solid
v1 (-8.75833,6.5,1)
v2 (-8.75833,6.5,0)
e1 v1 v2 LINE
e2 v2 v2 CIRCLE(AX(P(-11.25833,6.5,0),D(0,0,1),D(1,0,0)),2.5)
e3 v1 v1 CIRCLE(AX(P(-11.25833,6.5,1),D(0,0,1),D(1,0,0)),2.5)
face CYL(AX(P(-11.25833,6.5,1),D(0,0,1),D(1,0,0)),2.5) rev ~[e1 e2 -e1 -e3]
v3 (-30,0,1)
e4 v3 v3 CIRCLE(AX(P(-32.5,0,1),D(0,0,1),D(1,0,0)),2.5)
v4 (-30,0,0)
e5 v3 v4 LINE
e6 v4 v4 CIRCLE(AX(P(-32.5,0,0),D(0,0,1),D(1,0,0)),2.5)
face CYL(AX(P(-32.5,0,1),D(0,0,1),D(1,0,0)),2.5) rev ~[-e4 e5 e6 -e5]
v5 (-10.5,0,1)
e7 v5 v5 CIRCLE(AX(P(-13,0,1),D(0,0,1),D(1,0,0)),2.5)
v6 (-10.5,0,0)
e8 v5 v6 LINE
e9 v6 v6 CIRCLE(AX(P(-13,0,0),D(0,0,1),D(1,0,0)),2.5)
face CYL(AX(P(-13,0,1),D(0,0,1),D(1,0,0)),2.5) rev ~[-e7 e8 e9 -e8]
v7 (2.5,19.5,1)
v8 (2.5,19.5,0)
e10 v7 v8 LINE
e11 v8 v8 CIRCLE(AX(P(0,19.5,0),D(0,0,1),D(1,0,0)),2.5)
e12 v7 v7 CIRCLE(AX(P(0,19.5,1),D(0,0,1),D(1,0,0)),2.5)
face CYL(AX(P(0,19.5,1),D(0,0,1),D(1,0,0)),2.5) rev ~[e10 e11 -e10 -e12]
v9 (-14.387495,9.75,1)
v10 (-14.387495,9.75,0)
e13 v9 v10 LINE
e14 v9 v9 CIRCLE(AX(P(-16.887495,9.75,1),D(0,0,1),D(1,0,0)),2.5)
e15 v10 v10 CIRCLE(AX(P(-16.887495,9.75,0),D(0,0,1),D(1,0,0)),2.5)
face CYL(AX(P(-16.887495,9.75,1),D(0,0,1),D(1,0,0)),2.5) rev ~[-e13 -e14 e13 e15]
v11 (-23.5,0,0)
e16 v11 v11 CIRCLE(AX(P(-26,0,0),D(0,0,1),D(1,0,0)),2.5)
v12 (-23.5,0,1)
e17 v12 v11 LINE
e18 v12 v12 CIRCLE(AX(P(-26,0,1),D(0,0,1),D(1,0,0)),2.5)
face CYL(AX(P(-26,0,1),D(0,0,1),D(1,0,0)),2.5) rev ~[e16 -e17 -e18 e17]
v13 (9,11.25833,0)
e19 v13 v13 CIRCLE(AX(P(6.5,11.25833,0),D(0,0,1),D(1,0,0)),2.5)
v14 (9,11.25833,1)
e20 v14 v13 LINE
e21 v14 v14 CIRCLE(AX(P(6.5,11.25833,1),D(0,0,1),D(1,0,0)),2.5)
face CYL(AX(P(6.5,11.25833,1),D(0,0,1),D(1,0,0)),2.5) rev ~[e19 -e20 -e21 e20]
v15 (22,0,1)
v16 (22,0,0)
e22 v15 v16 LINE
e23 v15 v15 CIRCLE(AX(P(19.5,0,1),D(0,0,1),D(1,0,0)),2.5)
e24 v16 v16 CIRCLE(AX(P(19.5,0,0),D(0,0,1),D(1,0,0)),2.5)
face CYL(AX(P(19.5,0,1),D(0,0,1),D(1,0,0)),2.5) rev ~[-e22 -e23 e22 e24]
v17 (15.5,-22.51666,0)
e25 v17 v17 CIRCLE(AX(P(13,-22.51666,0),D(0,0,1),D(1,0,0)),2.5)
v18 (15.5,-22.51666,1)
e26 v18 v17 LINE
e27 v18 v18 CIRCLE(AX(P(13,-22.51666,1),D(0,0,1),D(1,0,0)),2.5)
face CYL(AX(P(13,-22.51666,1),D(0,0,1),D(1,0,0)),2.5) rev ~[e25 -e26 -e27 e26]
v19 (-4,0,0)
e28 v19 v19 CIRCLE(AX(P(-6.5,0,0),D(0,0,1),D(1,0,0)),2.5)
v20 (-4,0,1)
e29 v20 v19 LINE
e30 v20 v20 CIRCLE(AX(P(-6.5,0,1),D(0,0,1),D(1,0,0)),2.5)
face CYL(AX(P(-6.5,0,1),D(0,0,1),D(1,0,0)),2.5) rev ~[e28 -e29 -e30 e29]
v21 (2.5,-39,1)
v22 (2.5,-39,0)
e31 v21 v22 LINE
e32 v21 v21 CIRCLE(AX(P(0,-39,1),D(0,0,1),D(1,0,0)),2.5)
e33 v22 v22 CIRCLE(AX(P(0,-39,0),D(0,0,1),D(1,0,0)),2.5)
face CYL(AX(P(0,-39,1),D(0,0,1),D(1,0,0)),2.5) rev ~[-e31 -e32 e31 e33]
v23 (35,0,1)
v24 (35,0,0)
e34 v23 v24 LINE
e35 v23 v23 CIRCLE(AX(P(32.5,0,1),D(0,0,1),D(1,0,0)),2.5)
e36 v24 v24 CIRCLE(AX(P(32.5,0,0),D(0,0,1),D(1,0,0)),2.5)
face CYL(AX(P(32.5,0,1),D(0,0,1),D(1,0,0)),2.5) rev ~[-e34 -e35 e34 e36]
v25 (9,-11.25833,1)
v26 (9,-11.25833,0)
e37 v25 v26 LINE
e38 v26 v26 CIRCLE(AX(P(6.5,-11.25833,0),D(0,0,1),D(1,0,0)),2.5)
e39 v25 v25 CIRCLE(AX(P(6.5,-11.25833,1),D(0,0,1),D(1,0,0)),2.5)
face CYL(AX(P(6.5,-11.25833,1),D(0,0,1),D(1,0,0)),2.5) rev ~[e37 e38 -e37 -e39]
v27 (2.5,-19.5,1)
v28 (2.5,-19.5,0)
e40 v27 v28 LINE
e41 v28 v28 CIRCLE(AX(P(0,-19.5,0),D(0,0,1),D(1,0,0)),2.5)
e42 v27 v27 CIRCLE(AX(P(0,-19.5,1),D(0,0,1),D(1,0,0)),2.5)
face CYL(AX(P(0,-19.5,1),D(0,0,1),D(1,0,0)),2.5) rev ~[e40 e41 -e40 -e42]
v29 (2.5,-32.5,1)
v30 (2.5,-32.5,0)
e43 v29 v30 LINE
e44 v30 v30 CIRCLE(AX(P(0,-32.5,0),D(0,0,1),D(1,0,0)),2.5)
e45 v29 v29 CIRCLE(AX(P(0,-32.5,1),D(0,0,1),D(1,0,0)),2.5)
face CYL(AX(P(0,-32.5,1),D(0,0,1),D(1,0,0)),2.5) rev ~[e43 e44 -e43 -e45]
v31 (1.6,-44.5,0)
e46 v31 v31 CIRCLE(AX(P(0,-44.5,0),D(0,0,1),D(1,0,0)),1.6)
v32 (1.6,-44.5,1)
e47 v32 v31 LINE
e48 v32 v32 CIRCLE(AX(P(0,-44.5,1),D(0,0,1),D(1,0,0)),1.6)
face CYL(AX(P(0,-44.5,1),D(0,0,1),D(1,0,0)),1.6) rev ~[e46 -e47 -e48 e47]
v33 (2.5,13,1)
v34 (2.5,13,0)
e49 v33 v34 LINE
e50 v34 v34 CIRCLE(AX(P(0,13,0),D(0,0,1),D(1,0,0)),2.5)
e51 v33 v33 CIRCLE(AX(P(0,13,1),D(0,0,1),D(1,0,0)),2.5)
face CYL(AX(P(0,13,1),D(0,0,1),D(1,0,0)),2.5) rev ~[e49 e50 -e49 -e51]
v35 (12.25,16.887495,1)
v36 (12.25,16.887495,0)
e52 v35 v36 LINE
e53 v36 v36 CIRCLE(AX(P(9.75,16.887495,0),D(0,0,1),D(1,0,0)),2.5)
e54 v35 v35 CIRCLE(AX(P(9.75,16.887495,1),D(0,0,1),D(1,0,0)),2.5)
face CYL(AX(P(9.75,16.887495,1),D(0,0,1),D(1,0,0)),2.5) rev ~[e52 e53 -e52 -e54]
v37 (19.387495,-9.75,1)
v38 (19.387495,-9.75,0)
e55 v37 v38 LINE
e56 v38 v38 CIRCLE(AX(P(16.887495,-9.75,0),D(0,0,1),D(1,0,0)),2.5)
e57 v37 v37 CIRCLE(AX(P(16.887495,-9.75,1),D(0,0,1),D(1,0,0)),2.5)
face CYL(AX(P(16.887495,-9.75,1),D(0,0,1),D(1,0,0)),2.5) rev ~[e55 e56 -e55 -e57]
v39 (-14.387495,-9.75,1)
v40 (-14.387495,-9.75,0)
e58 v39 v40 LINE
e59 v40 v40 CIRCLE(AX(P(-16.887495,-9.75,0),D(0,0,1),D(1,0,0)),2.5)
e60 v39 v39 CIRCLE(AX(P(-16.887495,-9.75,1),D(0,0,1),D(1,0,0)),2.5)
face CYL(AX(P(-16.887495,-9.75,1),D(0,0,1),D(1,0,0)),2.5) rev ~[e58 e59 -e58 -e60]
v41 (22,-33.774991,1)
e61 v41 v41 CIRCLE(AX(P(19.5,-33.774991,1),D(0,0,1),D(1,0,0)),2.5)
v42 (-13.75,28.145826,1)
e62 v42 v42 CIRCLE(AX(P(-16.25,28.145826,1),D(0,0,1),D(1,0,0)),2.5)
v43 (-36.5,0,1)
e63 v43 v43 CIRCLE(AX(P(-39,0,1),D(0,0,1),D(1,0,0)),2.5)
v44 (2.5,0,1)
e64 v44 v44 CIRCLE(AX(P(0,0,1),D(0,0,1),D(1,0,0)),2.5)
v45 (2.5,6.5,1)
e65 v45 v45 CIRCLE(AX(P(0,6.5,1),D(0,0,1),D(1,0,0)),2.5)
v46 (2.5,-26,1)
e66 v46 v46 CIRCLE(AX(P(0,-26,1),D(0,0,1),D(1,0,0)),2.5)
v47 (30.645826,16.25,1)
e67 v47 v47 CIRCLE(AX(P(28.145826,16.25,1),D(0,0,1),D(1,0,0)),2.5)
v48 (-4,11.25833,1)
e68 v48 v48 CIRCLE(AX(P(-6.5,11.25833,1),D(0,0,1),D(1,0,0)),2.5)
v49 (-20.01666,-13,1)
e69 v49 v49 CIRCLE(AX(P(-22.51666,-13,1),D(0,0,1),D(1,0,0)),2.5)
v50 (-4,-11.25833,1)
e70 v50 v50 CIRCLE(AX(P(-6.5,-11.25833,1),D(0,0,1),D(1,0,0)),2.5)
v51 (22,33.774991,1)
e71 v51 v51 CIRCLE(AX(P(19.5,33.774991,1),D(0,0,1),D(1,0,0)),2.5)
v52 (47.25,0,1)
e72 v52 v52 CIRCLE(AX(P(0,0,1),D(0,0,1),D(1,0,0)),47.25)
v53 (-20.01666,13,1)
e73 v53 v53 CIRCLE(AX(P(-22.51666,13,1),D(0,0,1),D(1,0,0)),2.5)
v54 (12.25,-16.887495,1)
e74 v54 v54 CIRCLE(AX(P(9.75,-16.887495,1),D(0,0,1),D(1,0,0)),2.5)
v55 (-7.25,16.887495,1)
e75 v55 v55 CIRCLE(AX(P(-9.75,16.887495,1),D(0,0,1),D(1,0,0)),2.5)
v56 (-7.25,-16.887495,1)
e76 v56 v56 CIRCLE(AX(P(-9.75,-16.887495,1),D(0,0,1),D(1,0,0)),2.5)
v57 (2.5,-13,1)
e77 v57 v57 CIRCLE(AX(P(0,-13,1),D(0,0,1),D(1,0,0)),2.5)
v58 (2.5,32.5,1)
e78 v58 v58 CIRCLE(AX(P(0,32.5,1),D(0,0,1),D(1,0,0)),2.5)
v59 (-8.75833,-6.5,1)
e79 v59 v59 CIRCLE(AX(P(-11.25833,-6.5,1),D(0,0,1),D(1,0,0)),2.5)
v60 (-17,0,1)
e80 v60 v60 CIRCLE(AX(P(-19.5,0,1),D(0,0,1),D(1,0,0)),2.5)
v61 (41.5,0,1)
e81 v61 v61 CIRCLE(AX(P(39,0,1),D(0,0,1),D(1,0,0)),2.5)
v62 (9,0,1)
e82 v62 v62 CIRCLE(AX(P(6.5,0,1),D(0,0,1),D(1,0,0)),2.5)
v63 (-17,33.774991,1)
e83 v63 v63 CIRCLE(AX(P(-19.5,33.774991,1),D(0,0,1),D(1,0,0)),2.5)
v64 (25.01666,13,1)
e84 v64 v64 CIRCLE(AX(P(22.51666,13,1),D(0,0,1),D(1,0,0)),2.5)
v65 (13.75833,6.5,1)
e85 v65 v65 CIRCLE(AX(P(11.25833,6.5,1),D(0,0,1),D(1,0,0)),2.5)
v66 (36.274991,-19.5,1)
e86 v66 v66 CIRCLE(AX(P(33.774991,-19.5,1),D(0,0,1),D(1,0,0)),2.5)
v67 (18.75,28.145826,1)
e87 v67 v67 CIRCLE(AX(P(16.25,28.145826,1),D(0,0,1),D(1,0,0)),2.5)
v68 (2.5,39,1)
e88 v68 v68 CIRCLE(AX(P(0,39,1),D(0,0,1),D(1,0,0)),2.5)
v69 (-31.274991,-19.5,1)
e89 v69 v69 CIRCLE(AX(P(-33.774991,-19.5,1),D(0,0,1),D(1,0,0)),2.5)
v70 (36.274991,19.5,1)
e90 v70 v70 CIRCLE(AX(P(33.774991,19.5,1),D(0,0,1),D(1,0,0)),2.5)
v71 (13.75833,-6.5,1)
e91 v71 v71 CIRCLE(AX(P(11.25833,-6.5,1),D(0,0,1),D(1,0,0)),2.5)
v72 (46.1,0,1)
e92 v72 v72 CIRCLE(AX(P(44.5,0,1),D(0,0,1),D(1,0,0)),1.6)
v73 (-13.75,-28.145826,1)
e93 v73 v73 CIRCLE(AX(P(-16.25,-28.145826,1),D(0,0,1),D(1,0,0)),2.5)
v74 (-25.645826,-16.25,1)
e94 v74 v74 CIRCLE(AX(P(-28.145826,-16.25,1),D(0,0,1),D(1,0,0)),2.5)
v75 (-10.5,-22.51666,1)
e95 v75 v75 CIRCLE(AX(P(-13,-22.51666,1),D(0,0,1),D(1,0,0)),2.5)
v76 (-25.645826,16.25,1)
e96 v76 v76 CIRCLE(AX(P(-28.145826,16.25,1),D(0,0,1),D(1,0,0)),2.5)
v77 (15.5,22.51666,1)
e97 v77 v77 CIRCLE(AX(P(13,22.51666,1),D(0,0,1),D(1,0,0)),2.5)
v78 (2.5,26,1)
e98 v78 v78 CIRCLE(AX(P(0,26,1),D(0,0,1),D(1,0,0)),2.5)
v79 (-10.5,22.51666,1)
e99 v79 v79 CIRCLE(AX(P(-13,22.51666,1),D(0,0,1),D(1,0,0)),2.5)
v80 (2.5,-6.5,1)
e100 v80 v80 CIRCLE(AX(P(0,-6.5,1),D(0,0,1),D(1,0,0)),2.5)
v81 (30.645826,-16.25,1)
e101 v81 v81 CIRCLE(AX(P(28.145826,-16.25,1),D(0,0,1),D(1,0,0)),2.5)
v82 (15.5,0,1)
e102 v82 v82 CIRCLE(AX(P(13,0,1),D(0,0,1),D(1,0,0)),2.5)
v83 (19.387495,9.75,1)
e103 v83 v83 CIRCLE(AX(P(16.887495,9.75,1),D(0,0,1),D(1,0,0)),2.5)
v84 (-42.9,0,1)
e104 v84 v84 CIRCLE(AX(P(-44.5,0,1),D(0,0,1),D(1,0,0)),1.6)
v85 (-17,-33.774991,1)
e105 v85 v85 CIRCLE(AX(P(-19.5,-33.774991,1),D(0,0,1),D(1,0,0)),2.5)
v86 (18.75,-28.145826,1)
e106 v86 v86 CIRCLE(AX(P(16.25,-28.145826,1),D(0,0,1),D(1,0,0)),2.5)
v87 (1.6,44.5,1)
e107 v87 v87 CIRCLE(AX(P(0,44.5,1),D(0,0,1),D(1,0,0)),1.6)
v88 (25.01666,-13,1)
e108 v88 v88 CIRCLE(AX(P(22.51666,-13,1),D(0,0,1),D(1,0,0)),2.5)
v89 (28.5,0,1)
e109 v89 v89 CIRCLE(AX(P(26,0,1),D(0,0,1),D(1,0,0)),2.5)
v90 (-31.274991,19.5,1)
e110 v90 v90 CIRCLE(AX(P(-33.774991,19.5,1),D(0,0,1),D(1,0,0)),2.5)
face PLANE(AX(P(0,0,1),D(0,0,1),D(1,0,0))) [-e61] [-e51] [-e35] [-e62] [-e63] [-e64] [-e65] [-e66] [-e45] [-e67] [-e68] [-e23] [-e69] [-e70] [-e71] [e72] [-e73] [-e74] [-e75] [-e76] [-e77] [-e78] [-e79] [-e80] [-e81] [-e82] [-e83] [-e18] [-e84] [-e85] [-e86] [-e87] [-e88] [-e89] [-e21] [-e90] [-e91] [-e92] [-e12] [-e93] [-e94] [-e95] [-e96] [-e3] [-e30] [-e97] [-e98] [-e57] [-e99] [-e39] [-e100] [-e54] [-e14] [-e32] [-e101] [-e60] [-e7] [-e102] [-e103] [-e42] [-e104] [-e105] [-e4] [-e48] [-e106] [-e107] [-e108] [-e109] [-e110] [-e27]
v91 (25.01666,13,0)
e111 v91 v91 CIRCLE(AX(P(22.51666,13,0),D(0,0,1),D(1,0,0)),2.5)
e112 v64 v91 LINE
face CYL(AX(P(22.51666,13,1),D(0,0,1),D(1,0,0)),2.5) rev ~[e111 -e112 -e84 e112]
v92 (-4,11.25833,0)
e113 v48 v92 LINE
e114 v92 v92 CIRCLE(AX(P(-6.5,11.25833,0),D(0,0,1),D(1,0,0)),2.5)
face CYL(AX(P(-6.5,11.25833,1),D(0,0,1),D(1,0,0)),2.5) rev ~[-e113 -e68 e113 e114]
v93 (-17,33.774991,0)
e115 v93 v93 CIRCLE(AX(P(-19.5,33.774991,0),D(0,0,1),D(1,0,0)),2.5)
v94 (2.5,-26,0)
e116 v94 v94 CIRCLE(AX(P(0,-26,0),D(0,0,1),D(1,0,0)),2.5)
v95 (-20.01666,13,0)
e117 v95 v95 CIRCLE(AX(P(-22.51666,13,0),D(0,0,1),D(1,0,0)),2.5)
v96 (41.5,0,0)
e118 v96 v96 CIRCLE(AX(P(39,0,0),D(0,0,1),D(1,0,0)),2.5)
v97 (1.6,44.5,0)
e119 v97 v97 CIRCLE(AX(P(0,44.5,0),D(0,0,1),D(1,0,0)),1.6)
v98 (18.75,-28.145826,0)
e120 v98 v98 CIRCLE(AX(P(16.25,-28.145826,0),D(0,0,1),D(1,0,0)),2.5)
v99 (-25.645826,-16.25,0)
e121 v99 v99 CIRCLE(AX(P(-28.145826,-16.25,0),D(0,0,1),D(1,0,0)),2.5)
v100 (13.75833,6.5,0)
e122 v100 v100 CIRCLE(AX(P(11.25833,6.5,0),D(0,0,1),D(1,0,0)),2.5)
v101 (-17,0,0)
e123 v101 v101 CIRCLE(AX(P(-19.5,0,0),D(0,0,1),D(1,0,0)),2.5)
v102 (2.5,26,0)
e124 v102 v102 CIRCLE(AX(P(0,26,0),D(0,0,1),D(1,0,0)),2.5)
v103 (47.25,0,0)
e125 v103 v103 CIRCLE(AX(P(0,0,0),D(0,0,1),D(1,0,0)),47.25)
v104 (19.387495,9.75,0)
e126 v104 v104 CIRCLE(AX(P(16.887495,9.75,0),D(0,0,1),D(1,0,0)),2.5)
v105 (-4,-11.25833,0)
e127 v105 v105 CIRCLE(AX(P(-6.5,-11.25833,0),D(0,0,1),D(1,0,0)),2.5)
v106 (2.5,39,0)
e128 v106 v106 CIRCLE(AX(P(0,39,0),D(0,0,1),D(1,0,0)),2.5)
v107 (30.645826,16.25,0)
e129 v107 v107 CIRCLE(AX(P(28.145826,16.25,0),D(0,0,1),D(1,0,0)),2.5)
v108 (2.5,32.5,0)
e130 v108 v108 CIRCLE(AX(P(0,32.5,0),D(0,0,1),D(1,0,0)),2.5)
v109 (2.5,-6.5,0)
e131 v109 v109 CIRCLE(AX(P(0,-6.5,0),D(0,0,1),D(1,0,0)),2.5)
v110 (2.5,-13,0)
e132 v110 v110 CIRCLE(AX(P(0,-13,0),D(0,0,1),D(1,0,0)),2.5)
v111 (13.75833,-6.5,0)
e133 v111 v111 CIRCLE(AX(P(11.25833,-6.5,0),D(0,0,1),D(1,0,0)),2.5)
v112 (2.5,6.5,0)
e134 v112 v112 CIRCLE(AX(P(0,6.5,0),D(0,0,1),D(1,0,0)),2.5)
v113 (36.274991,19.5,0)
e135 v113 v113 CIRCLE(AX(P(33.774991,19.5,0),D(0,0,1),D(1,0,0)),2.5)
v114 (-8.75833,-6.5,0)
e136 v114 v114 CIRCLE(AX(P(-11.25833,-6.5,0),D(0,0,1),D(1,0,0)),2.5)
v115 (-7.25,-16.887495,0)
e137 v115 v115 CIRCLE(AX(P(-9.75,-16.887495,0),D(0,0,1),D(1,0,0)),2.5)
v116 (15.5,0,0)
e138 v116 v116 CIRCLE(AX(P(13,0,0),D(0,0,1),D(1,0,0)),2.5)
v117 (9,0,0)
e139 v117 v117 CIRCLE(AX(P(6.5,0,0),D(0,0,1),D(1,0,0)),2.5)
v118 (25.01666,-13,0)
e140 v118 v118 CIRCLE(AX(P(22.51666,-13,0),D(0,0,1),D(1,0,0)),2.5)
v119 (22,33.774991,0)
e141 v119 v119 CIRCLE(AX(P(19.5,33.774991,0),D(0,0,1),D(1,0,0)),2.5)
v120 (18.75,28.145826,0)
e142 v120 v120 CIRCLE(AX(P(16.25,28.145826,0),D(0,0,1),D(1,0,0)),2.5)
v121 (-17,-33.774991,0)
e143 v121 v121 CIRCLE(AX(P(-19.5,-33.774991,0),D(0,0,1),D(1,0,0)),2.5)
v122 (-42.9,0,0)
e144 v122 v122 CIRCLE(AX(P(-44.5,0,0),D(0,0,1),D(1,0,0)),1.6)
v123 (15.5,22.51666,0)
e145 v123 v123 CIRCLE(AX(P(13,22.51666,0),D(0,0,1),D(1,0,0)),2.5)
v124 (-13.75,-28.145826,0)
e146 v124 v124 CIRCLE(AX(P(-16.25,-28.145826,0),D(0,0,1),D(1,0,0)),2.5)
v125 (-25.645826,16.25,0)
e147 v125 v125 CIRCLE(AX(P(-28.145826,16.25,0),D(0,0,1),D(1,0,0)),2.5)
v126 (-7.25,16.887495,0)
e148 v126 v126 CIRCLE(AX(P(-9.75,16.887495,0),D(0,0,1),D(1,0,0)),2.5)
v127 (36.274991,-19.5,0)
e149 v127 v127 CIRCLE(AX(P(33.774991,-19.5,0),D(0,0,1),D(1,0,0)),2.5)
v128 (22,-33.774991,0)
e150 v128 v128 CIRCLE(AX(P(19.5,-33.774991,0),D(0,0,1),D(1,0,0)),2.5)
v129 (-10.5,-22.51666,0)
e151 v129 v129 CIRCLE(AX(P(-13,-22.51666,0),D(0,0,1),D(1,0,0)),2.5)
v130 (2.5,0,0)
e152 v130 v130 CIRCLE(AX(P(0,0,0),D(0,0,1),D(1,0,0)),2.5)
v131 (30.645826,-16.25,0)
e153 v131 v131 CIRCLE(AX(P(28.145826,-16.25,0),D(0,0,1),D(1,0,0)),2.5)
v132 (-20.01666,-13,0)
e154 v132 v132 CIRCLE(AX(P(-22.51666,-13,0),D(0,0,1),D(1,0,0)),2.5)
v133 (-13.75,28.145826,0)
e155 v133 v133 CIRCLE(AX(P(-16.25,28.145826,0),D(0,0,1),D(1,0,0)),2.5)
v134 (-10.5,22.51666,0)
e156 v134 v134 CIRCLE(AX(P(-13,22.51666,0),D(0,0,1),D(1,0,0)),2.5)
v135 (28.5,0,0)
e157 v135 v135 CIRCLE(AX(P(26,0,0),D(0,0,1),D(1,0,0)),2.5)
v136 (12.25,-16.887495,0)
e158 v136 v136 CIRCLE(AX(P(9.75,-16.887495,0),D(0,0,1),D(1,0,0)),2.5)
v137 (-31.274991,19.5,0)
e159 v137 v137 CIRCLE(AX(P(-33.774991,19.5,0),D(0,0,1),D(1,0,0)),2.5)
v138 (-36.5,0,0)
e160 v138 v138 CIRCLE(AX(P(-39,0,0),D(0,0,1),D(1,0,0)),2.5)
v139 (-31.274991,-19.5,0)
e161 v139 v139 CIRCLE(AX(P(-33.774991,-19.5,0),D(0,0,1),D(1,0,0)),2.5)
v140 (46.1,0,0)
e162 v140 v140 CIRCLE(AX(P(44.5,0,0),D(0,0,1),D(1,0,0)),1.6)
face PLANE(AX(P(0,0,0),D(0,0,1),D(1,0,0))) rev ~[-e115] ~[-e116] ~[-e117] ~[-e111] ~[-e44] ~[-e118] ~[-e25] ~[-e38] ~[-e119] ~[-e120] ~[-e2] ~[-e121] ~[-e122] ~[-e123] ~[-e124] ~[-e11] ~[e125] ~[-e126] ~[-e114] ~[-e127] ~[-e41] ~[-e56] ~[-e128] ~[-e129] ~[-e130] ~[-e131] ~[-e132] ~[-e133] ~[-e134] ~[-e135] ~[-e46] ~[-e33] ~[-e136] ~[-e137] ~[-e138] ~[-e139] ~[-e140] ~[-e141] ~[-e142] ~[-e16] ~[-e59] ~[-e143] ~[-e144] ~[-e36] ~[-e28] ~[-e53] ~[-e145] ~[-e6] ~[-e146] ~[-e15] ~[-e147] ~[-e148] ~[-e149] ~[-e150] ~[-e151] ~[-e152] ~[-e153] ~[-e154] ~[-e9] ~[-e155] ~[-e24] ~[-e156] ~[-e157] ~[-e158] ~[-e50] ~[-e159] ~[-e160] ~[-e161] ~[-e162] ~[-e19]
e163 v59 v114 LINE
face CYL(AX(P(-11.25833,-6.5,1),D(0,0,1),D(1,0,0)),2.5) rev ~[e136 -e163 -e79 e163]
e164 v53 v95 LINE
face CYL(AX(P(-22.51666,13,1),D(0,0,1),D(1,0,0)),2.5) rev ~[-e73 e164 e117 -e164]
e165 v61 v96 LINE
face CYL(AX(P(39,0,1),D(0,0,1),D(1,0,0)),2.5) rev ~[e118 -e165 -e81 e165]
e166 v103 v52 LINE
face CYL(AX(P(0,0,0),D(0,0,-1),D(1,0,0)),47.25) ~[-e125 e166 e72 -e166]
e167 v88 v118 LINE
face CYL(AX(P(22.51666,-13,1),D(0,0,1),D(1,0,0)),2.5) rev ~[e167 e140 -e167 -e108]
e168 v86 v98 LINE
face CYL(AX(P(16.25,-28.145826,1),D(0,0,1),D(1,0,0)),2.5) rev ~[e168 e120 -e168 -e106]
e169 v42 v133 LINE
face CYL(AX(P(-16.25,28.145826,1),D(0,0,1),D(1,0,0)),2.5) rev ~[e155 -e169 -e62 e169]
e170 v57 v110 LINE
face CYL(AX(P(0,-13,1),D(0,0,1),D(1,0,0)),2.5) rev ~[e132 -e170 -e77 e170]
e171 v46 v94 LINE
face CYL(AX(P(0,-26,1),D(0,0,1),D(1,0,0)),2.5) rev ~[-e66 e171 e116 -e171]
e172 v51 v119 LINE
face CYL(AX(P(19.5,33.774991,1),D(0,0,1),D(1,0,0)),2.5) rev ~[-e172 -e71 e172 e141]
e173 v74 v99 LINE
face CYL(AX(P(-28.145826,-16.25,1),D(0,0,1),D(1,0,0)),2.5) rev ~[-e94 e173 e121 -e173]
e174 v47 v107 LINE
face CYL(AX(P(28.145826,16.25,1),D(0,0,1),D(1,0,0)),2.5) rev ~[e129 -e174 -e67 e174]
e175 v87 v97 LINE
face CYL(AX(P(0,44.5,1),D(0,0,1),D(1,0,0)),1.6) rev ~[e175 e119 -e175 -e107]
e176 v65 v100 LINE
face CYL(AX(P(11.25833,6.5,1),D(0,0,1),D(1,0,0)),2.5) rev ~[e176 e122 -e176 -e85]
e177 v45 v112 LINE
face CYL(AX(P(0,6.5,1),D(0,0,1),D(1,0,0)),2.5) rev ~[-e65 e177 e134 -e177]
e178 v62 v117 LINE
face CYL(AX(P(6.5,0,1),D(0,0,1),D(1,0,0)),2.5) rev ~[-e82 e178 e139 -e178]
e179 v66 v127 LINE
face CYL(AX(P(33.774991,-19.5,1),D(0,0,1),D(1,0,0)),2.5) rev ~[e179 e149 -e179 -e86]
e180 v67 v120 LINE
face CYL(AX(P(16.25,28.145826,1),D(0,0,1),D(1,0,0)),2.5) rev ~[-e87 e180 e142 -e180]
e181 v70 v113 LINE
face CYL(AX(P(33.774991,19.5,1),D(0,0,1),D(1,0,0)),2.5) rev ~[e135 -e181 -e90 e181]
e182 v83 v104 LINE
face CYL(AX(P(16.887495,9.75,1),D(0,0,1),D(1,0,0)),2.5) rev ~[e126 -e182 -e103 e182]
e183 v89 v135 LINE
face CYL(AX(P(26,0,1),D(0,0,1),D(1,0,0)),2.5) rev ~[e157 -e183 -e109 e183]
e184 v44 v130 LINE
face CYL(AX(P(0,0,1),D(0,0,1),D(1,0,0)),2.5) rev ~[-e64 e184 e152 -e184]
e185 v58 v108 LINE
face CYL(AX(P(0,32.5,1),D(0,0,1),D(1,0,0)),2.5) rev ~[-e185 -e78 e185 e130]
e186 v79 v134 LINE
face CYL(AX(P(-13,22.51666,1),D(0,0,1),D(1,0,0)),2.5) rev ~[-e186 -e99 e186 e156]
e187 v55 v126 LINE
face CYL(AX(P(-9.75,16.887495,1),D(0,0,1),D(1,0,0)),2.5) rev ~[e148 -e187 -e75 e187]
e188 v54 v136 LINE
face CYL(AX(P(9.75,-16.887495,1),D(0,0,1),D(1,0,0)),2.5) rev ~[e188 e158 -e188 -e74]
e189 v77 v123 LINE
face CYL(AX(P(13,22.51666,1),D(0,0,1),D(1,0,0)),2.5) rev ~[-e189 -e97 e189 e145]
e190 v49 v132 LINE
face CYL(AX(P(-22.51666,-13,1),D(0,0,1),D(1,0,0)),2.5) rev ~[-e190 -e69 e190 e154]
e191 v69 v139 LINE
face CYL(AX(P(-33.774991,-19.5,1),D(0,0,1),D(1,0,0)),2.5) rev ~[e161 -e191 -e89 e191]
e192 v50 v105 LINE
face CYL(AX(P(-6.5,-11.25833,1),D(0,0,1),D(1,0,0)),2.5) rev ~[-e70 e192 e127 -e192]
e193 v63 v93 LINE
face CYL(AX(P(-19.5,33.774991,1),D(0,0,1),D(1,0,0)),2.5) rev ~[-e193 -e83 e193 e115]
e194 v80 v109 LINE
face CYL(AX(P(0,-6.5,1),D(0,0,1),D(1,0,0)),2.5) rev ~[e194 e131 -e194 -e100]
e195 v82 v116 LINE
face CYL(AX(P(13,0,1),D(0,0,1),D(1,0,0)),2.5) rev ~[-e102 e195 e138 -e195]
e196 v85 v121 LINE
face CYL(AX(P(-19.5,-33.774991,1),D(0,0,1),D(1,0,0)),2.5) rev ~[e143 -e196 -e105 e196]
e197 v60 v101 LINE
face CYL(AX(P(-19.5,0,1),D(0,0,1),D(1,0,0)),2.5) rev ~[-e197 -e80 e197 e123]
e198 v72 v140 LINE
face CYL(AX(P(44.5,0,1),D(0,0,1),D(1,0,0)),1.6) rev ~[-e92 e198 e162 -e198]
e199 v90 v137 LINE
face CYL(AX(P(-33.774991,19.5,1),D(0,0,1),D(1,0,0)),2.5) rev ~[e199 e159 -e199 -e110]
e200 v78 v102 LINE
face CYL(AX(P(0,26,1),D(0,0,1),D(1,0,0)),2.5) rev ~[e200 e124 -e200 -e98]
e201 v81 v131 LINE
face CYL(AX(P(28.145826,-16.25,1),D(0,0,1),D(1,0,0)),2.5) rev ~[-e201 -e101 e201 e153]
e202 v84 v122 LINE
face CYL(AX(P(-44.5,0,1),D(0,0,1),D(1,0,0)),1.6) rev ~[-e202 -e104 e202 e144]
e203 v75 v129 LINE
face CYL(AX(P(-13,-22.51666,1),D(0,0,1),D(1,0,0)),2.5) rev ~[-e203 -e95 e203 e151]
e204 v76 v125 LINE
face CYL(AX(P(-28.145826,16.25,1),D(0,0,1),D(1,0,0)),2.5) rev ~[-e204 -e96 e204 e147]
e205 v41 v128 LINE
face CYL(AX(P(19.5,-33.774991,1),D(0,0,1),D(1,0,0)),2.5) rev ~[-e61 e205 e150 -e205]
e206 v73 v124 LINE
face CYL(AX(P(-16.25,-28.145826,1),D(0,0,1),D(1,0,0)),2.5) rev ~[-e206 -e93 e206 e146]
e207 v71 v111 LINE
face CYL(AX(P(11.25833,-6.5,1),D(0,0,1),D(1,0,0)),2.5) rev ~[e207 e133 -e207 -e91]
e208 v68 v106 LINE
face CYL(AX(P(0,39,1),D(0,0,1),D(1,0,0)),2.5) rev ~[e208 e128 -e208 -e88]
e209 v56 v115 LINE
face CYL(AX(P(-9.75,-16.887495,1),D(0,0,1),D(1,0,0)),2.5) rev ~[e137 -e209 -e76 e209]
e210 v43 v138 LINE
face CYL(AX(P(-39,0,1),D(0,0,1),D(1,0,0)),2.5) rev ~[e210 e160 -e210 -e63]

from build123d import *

# Parameters (mm, degrees)
SKETCH_1_R          = 47.25
EXTRUDE_1_DEPTH     = 1
SKETCH_6_R          = 2.5
CUT_EXTRUDE_3_DEPTH = 2
SKETCH_7_R          = 1.6
CUT_EXTRUDE_4_DEPTH = 2


with BuildPart() as part:
    # 草图1 → 凸台-拉伸1 (new body)
    with BuildSketch(Plane.XY):
        Circle(SKETCH_1_R)
    extrude(amount=EXTRUDE_1_DEPTH)

    # 草图6 → 切除-拉伸3 (cut)
    with BuildSketch(Plane.XY.offset(1)):
        with Locations((0, 6.5)):
            Circle(SKETCH_6_R)
        with Locations((0, 13)):
            Circle(SKETCH_6_R)
        with Locations((0, 19.5)):
            Circle(SKETCH_6_R)
        with Locations((0, 26)):
            Circle(SKETCH_6_R)
        with Locations((0, 32.5)):
            Circle(SKETCH_6_R)
        with Locations((0, 39)):
            Circle(SKETCH_6_R)
        Circle(SKETCH_6_R)
        with Locations((19.5, 33.774990748)):
            Circle(SKETCH_6_R)
        with Locations((16.25, 28.145825623)):
            Circle(SKETCH_6_R)
        with Locations((13, 22.516660498)):
            Circle(SKETCH_6_R)
        with Locations((9.75, 16.887495374)):
            Circle(SKETCH_6_R)
        with Locations((6.5, 11.258330249)):
            Circle(SKETCH_6_R)
        with Locations((33.774990748, 19.5)):
            Circle(SKETCH_6_R)
        with Locations((28.145825623, 16.25)):
            Circle(SKETCH_6_R)
        with Locations((22.516660498, 13)):
            Circle(SKETCH_6_R)
        with Locations((16.887495374, 9.75)):
            Circle(SKETCH_6_R)
        with Locations((11.258330249, 6.5)):
            Circle(SKETCH_6_R)
        with Locations((39, 0)):
            Circle(SKETCH_6_R)
        with Locations((32.5, 0)):
            Circle(SKETCH_6_R)
        with Locations((26, 0)):
            Circle(SKETCH_6_R)
        with Locations((19.5, 0)):
            Circle(SKETCH_6_R)
        with Locations((13, 0)):
            Circle(SKETCH_6_R)
        with Locations((33.774990748, -19.5)):
            Circle(SKETCH_6_R)
        with Locations((28.145825623, -16.25)):
            Circle(SKETCH_6_R)
        with Locations((22.516660498, -13)):
            Circle(SKETCH_6_R)
        with Locations((16.887495374, -9.75)):
            Circle(SKETCH_6_R)
        with Locations((11.258330249, -6.5)):
            Circle(SKETCH_6_R)
        with Locations((19.5, -33.774990748)):
            Circle(SKETCH_6_R)
        with Locations((16.25, -28.145825623)):
            Circle(SKETCH_6_R)
        with Locations((13, -22.516660498)):
            Circle(SKETCH_6_R)
        with Locations((9.75, -16.887495374)):
            Circle(SKETCH_6_R)
        with Locations((6.5, -11.258330249)):
            Circle(SKETCH_6_R)
        with Locations((0, -39)):
            Circle(SKETCH_6_R)
        with Locations((0, -32.5)):
            Circle(SKETCH_6_R)
        with Locations((0, -26)):
            Circle(SKETCH_6_R)
        with Locations((0, -19.5)):
            Circle(SKETCH_6_R)
        with Locations((0, -13)):
            Circle(SKETCH_6_R)
        with Locations((-19.5, -33.774990748)):
            Circle(SKETCH_6_R)
        with Locations((-16.25, -28.145825623)):
            Circle(SKETCH_6_R)
        with Locations((-13, -22.516660498)):
            Circle(SKETCH_6_R)
        with Locations((-9.75, -16.887495374)):
            Circle(SKETCH_6_R)
        with Locations((-6.5, -11.258330249)):
            Circle(SKETCH_6_R)
        with Locations((-33.774990748, -19.5)):
            Circle(SKETCH_6_R)
        with Locations((-28.145825623, -16.25)):
            Circle(SKETCH_6_R)
        with Locations((-22.516660498, -13)):
            Circle(SKETCH_6_R)
        with Locations((-16.887495374, -9.75)):
            Circle(SKETCH_6_R)
        with Locations((-11.258330249, -6.5)):
            Circle(SKETCH_6_R)
        with Locations((-39, 0)):
            Circle(SKETCH_6_R)
        with Locations((-32.5, 0)):
            Circle(SKETCH_6_R)
        with Locations((-26, 0)):
            Circle(SKETCH_6_R)
        with Locations((-19.5, 0)):
            Circle(SKETCH_6_R)
        with Locations((-13, 0)):
            Circle(SKETCH_6_R)
        with Locations((-33.774990748, 19.5)):
            Circle(SKETCH_6_R)
        with Locations((-28.145825623, 16.25)):
            Circle(SKETCH_6_R)
        with Locations((-22.516660498, 13)):
            Circle(SKETCH_6_R)
        with Locations((-16.887495374, 9.75)):
            Circle(SKETCH_6_R)
        with Locations((-11.258330249, 6.5)):
            Circle(SKETCH_6_R)
        with Locations((-19.5, 33.774990748)):
            Circle(SKETCH_6_R)
        with Locations((-16.25, 28.145825623)):
            Circle(SKETCH_6_R)
        with Locations((-13, 22.516660498)):
            Circle(SKETCH_6_R)
        with Locations((-9.75, 16.887495374)):
            Circle(SKETCH_6_R)
        with Locations((-6.5, 11.258330249)):
            Circle(SKETCH_6_R)
        with Locations((6.5, 0)):
            Circle(SKETCH_6_R)
        with Locations((0, -6.5)):
            Circle(SKETCH_6_R)
        with Locations((-6.5, 0)):
            Circle(SKETCH_6_R)
    extrude(amount=-CUT_EXTRUDE_3_DEPTH, mode=Mode.SUBTRACT)

    # 草图7 → 切除-拉伸4 (cut)
    with BuildSketch(Plane.XY.offset(1)):
        with Locations((0, -44.5)):
            Circle(SKETCH_7_R)
        with Locations((44.5, 0)):
            Circle(SKETCH_7_R)
        with Locations((-44.5, 0)):
            Circle(SKETCH_7_R)
        with Locations((0, 44.5)):
            Circle(SKETCH_7_R)
    extrude(amount=-CUT_EXTRUDE_4_DEPTH, mode=Mode.SUBTRACT)


solid = part.part
